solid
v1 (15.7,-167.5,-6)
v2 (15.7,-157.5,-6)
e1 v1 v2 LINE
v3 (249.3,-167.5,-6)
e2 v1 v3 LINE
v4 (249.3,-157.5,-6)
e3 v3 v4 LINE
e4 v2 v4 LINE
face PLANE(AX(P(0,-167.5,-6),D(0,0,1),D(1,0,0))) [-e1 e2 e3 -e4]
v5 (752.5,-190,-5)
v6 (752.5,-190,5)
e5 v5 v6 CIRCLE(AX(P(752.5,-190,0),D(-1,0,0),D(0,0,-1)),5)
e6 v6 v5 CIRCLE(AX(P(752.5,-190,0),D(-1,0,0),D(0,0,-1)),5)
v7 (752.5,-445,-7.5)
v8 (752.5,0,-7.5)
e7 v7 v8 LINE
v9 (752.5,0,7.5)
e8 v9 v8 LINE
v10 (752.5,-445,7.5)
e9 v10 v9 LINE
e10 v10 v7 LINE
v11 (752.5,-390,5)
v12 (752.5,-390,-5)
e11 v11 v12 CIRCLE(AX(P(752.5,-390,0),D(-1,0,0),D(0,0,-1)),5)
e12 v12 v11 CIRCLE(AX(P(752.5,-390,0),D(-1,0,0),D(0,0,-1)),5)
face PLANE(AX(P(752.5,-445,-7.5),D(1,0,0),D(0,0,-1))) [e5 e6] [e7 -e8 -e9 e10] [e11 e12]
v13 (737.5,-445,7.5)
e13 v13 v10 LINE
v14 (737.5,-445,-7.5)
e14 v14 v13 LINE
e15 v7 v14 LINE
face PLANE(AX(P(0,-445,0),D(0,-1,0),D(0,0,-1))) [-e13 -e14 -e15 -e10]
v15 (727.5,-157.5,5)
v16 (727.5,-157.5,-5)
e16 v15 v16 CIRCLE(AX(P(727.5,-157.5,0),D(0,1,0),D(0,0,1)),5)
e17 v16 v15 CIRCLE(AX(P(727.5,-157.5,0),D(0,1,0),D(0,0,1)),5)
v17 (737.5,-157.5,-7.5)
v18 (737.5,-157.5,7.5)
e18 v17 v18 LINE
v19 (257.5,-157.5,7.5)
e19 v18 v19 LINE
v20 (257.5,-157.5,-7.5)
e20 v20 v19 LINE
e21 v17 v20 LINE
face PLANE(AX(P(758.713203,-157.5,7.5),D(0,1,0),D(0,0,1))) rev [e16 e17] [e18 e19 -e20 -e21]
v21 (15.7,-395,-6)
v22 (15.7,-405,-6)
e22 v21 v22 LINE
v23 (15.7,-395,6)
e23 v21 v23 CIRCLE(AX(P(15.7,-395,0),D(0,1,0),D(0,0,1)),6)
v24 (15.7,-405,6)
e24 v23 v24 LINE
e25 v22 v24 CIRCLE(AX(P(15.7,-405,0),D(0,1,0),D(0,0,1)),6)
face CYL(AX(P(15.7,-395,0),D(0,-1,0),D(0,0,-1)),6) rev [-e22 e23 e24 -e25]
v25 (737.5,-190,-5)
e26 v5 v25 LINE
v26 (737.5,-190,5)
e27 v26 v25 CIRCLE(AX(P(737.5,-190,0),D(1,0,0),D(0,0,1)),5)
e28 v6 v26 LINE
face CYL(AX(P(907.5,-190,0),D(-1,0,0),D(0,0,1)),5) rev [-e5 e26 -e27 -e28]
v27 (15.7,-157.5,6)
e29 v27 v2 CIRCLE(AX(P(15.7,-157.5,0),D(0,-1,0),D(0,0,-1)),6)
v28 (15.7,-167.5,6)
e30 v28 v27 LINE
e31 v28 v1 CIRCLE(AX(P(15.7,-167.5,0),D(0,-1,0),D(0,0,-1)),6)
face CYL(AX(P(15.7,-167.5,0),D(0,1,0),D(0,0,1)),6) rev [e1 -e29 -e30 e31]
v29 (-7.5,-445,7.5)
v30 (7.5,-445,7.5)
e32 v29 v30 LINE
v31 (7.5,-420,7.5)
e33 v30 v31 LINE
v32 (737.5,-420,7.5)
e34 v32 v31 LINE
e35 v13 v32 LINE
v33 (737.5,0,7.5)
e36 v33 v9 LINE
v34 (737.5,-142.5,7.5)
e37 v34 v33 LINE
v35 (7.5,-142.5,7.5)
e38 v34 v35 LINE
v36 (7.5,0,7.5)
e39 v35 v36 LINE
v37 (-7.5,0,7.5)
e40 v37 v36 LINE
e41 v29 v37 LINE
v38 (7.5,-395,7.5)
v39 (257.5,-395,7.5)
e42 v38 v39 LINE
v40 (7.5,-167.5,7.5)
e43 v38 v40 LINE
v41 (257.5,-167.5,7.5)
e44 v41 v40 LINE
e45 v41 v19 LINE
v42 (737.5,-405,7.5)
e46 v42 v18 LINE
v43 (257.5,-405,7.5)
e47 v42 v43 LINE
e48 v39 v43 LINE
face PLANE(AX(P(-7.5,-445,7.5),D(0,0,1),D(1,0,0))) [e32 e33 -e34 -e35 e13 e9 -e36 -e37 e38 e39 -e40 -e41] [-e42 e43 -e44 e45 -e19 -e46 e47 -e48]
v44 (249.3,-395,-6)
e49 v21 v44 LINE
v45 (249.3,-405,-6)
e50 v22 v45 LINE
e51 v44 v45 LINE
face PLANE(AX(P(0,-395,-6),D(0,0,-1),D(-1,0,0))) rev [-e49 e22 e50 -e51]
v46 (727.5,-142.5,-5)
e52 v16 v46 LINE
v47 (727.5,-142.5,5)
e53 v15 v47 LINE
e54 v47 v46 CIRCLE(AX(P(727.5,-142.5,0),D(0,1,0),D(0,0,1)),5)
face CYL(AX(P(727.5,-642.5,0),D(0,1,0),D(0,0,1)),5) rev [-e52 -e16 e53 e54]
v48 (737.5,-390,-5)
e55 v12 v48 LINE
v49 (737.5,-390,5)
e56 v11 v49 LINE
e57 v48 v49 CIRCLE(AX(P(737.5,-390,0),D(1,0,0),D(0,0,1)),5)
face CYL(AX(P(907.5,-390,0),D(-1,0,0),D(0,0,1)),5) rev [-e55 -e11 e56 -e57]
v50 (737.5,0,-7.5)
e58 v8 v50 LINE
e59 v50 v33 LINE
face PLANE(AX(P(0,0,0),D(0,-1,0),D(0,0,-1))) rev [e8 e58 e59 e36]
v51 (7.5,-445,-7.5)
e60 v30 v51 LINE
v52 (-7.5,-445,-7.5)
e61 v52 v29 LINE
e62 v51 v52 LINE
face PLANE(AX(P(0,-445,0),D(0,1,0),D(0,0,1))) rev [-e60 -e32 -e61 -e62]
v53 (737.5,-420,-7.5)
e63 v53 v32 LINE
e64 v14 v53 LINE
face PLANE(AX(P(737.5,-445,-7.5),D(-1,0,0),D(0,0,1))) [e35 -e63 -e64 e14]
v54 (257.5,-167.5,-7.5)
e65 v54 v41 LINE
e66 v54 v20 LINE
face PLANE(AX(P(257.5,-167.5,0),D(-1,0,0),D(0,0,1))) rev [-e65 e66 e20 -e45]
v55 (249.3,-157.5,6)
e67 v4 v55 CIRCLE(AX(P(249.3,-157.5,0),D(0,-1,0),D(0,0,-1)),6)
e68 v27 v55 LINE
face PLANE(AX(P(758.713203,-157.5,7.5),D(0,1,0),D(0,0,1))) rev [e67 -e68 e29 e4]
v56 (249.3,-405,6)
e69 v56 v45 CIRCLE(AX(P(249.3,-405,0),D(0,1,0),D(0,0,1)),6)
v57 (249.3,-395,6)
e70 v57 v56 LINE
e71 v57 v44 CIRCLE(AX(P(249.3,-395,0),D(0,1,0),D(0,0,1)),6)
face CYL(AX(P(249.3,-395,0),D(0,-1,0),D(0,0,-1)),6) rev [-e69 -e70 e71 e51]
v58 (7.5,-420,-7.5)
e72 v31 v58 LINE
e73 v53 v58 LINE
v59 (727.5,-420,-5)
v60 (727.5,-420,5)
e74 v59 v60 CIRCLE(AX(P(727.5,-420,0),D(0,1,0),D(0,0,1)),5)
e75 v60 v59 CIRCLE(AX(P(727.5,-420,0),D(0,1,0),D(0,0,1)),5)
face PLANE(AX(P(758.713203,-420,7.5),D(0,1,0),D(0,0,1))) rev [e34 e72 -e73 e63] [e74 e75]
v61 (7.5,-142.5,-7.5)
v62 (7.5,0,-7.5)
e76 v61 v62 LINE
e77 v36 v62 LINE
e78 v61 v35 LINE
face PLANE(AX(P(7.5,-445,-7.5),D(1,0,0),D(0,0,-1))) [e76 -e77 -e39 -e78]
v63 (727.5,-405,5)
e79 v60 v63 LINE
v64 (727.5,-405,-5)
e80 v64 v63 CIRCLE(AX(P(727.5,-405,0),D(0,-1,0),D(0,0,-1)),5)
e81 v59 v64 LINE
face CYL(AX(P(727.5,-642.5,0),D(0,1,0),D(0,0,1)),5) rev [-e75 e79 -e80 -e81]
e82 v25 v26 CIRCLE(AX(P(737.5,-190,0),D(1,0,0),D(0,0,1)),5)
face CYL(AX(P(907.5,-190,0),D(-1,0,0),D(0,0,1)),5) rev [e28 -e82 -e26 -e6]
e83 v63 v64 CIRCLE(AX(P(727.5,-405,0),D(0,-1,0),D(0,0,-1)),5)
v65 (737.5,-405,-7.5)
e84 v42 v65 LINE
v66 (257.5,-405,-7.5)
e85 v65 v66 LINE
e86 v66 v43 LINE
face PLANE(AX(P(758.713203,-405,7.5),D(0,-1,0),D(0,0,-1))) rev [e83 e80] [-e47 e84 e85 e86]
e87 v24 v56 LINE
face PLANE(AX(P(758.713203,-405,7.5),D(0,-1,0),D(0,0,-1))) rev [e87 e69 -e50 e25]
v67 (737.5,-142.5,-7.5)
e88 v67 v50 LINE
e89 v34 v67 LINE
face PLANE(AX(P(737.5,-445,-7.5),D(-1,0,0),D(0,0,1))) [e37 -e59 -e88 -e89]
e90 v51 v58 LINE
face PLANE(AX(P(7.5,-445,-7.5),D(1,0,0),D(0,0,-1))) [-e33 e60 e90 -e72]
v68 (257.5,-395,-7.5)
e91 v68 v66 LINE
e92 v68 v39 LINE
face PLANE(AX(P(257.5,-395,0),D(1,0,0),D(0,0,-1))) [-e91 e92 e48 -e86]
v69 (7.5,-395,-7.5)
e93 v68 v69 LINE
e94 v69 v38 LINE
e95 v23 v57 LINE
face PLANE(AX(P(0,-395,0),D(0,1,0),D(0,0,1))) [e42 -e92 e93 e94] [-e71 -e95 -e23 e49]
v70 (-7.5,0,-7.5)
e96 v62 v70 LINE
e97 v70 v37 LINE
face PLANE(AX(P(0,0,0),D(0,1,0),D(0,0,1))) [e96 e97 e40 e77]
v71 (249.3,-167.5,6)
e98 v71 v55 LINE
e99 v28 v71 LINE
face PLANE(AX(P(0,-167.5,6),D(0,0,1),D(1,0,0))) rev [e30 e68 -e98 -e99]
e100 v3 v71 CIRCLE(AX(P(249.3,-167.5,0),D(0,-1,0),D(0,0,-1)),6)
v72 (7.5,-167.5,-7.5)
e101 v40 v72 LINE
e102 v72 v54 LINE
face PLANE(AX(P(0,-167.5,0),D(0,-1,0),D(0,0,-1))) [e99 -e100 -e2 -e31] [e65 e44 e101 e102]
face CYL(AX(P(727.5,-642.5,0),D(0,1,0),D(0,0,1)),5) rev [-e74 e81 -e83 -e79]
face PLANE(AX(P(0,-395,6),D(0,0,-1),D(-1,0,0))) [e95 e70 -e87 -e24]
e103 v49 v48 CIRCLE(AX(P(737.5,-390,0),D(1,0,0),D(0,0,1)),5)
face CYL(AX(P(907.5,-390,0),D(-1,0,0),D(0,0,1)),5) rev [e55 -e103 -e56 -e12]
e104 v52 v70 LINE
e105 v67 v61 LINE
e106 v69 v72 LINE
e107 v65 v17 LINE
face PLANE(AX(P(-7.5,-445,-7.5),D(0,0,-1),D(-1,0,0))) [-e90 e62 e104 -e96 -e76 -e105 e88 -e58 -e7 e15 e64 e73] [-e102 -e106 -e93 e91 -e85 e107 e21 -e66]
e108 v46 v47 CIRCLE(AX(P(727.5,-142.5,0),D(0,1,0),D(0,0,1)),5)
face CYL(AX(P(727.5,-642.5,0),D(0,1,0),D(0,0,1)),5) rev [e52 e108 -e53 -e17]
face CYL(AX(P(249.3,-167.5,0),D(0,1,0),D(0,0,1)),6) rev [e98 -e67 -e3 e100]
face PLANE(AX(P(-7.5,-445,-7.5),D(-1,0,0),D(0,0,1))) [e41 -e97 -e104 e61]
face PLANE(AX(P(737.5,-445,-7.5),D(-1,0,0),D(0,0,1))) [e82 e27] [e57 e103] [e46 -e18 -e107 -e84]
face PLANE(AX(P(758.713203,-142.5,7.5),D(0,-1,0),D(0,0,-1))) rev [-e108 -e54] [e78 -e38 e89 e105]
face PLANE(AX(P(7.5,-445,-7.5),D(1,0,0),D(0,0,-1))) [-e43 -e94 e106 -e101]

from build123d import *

# Parameters (mm, degrees)
SKETCH1_W             = 15
SKETCH1_H             = 15
BOSS_EXTRUDE1_DEPTH   = 445
BOSS_EXTRUDE1_2_DEPTH = 445
SKETCH2_W             = 15
SKETCH2_H             = 15
BOSS_EXTRUDE2_DEPTH   = 730
SKETCH3_R             = 5
CUT_EXTRUDE1_DEPTH    = 900
SKETCH4_W             = 250
SKETCH4_H             = 15
BOSS_EXTRUDE5_DEPTH   = 10
BOSS_EXTRUDE6_START   = 10
SKETCH6_W             = 250
SKETCH6_H             = 15
BOSS_EXTRUDE6_DEPTH   = 10
SKETCH7_R             = 5
CUT_EXTRUDE2_DEPTH    = 500


with BuildPart() as part:
    # Sketch1 → Boss-Extrude1 (new body)
    with BuildSketch(Plane(origin=(0, 0, 0), x_dir=(1, 0, 0), z_dir=(0, 1, 0))):
        Rectangle(SKETCH1_W, SKETCH1_H)
    extrude(amount=-BOSS_EXTRUDE1_DEPTH)



with BuildPart() as body_2:
    # Sketch1 → Boss-Extrude1 2 (new body)
    with BuildSketch(Plane(origin=(0, 0, 0), x_dir=(1, 0, 0), z_dir=(0, 1, 0))):
        with Locations((745, 0)):
            Rectangle(SKETCH1_W, SKETCH1_H)
    extrude(amount=-BOSS_EXTRUDE1_2_DEPTH)


with BuildPart() as part_1:
    add(part.part)

    add(body_2.part)  # Boss-Extrude2 merges body 2
    # Sketch2 → Boss-Extrude2 (add)
    with BuildSketch(Plane(origin=(7.5, 0, 0), x_dir=(0, 0, -1), z_dir=(1, 0, 0))):
        with Locations((0, -412.5)):
            Rectangle(SKETCH2_W, SKETCH2_H)
        with Locations((0, -150)):
            Rectangle(SKETCH2_W, SKETCH2_H)
    extrude(amount=BOSS_EXTRUDE2_DEPTH)

    # Sketch3 → Cut-Extrude1 (cut)
    with BuildSketch(Plane(origin=(7.5, 0, 0), x_dir=(0, 0, -1), z_dir=(1, 0, 0))):
        with Locations(Location((0, -190, 0), (0, 0, 180))):
            Circle(SKETCH3_R)
        with Locations(Location((0, -390, 0), (0, 0, 180))):
            Circle(SKETCH3_R)
    extrude(amount=CUT_EXTRUDE1_DEPTH, mode=Mode.SUBTRACT)

    # Sketch4 → Boss-Extrude5 (add)
    with BuildSketch(Plane(origin=(0, -405, 0), x_dir=(1, 0, 0), z_dir=(0, 1, 0))):
        with Locations((132.5, 0)):
            Rectangle(SKETCH4_W, SKETCH4_H)
        with BuildLine():
            ThreePointArc((15.7, -6), (9.7, 0), (15.7, 6))
            Line((15.7, 6), (249.3, 6))
            ThreePointArc((249.3, 6), (255.3, 0), (249.3, -6))
            Line((249.3, -6), (15.7, -6))
        make_face(mode=Mode.SUBTRACT)
    extrude(amount=BOSS_EXTRUDE5_DEPTH)

    # Sketch6 → Boss-Extrude6 (add)
    with BuildSketch(Plane.XZ.offset(157.5).offset(BOSS_EXTRUDE6_START)):
        with Locations((132.5, 0)):
            Rectangle(SKETCH6_W, SKETCH6_H)
        with BuildLine():
            ThreePointArc((15.7, -6), (9.7, 0), (15.7, 6))
            Line((15.7, 6), (249.3, 6))
            ThreePointArc((249.3, 6), (255.3, 0), (249.3, -6))
            Line((249.3, -6), (15.7, -6))
        make_face(mode=Mode.SUBTRACT)
    extrude(amount=-BOSS_EXTRUDE6_DEPTH)

    # Sketch7 → Cut-Extrude2 (cut)
    with BuildSketch(Plane(origin=(0, -142.5, 0), x_dir=(1, 0, 0), z_dir=(0, 1, 0))):
        with Locations(Location((727.5, 0, 0), (0, 0, 270))):
            Circle(SKETCH7_R)
    extrude(amount=-CUT_EXTRUDE2_DEPTH, mode=Mode.SUBTRACT)


solid = part_1.part
